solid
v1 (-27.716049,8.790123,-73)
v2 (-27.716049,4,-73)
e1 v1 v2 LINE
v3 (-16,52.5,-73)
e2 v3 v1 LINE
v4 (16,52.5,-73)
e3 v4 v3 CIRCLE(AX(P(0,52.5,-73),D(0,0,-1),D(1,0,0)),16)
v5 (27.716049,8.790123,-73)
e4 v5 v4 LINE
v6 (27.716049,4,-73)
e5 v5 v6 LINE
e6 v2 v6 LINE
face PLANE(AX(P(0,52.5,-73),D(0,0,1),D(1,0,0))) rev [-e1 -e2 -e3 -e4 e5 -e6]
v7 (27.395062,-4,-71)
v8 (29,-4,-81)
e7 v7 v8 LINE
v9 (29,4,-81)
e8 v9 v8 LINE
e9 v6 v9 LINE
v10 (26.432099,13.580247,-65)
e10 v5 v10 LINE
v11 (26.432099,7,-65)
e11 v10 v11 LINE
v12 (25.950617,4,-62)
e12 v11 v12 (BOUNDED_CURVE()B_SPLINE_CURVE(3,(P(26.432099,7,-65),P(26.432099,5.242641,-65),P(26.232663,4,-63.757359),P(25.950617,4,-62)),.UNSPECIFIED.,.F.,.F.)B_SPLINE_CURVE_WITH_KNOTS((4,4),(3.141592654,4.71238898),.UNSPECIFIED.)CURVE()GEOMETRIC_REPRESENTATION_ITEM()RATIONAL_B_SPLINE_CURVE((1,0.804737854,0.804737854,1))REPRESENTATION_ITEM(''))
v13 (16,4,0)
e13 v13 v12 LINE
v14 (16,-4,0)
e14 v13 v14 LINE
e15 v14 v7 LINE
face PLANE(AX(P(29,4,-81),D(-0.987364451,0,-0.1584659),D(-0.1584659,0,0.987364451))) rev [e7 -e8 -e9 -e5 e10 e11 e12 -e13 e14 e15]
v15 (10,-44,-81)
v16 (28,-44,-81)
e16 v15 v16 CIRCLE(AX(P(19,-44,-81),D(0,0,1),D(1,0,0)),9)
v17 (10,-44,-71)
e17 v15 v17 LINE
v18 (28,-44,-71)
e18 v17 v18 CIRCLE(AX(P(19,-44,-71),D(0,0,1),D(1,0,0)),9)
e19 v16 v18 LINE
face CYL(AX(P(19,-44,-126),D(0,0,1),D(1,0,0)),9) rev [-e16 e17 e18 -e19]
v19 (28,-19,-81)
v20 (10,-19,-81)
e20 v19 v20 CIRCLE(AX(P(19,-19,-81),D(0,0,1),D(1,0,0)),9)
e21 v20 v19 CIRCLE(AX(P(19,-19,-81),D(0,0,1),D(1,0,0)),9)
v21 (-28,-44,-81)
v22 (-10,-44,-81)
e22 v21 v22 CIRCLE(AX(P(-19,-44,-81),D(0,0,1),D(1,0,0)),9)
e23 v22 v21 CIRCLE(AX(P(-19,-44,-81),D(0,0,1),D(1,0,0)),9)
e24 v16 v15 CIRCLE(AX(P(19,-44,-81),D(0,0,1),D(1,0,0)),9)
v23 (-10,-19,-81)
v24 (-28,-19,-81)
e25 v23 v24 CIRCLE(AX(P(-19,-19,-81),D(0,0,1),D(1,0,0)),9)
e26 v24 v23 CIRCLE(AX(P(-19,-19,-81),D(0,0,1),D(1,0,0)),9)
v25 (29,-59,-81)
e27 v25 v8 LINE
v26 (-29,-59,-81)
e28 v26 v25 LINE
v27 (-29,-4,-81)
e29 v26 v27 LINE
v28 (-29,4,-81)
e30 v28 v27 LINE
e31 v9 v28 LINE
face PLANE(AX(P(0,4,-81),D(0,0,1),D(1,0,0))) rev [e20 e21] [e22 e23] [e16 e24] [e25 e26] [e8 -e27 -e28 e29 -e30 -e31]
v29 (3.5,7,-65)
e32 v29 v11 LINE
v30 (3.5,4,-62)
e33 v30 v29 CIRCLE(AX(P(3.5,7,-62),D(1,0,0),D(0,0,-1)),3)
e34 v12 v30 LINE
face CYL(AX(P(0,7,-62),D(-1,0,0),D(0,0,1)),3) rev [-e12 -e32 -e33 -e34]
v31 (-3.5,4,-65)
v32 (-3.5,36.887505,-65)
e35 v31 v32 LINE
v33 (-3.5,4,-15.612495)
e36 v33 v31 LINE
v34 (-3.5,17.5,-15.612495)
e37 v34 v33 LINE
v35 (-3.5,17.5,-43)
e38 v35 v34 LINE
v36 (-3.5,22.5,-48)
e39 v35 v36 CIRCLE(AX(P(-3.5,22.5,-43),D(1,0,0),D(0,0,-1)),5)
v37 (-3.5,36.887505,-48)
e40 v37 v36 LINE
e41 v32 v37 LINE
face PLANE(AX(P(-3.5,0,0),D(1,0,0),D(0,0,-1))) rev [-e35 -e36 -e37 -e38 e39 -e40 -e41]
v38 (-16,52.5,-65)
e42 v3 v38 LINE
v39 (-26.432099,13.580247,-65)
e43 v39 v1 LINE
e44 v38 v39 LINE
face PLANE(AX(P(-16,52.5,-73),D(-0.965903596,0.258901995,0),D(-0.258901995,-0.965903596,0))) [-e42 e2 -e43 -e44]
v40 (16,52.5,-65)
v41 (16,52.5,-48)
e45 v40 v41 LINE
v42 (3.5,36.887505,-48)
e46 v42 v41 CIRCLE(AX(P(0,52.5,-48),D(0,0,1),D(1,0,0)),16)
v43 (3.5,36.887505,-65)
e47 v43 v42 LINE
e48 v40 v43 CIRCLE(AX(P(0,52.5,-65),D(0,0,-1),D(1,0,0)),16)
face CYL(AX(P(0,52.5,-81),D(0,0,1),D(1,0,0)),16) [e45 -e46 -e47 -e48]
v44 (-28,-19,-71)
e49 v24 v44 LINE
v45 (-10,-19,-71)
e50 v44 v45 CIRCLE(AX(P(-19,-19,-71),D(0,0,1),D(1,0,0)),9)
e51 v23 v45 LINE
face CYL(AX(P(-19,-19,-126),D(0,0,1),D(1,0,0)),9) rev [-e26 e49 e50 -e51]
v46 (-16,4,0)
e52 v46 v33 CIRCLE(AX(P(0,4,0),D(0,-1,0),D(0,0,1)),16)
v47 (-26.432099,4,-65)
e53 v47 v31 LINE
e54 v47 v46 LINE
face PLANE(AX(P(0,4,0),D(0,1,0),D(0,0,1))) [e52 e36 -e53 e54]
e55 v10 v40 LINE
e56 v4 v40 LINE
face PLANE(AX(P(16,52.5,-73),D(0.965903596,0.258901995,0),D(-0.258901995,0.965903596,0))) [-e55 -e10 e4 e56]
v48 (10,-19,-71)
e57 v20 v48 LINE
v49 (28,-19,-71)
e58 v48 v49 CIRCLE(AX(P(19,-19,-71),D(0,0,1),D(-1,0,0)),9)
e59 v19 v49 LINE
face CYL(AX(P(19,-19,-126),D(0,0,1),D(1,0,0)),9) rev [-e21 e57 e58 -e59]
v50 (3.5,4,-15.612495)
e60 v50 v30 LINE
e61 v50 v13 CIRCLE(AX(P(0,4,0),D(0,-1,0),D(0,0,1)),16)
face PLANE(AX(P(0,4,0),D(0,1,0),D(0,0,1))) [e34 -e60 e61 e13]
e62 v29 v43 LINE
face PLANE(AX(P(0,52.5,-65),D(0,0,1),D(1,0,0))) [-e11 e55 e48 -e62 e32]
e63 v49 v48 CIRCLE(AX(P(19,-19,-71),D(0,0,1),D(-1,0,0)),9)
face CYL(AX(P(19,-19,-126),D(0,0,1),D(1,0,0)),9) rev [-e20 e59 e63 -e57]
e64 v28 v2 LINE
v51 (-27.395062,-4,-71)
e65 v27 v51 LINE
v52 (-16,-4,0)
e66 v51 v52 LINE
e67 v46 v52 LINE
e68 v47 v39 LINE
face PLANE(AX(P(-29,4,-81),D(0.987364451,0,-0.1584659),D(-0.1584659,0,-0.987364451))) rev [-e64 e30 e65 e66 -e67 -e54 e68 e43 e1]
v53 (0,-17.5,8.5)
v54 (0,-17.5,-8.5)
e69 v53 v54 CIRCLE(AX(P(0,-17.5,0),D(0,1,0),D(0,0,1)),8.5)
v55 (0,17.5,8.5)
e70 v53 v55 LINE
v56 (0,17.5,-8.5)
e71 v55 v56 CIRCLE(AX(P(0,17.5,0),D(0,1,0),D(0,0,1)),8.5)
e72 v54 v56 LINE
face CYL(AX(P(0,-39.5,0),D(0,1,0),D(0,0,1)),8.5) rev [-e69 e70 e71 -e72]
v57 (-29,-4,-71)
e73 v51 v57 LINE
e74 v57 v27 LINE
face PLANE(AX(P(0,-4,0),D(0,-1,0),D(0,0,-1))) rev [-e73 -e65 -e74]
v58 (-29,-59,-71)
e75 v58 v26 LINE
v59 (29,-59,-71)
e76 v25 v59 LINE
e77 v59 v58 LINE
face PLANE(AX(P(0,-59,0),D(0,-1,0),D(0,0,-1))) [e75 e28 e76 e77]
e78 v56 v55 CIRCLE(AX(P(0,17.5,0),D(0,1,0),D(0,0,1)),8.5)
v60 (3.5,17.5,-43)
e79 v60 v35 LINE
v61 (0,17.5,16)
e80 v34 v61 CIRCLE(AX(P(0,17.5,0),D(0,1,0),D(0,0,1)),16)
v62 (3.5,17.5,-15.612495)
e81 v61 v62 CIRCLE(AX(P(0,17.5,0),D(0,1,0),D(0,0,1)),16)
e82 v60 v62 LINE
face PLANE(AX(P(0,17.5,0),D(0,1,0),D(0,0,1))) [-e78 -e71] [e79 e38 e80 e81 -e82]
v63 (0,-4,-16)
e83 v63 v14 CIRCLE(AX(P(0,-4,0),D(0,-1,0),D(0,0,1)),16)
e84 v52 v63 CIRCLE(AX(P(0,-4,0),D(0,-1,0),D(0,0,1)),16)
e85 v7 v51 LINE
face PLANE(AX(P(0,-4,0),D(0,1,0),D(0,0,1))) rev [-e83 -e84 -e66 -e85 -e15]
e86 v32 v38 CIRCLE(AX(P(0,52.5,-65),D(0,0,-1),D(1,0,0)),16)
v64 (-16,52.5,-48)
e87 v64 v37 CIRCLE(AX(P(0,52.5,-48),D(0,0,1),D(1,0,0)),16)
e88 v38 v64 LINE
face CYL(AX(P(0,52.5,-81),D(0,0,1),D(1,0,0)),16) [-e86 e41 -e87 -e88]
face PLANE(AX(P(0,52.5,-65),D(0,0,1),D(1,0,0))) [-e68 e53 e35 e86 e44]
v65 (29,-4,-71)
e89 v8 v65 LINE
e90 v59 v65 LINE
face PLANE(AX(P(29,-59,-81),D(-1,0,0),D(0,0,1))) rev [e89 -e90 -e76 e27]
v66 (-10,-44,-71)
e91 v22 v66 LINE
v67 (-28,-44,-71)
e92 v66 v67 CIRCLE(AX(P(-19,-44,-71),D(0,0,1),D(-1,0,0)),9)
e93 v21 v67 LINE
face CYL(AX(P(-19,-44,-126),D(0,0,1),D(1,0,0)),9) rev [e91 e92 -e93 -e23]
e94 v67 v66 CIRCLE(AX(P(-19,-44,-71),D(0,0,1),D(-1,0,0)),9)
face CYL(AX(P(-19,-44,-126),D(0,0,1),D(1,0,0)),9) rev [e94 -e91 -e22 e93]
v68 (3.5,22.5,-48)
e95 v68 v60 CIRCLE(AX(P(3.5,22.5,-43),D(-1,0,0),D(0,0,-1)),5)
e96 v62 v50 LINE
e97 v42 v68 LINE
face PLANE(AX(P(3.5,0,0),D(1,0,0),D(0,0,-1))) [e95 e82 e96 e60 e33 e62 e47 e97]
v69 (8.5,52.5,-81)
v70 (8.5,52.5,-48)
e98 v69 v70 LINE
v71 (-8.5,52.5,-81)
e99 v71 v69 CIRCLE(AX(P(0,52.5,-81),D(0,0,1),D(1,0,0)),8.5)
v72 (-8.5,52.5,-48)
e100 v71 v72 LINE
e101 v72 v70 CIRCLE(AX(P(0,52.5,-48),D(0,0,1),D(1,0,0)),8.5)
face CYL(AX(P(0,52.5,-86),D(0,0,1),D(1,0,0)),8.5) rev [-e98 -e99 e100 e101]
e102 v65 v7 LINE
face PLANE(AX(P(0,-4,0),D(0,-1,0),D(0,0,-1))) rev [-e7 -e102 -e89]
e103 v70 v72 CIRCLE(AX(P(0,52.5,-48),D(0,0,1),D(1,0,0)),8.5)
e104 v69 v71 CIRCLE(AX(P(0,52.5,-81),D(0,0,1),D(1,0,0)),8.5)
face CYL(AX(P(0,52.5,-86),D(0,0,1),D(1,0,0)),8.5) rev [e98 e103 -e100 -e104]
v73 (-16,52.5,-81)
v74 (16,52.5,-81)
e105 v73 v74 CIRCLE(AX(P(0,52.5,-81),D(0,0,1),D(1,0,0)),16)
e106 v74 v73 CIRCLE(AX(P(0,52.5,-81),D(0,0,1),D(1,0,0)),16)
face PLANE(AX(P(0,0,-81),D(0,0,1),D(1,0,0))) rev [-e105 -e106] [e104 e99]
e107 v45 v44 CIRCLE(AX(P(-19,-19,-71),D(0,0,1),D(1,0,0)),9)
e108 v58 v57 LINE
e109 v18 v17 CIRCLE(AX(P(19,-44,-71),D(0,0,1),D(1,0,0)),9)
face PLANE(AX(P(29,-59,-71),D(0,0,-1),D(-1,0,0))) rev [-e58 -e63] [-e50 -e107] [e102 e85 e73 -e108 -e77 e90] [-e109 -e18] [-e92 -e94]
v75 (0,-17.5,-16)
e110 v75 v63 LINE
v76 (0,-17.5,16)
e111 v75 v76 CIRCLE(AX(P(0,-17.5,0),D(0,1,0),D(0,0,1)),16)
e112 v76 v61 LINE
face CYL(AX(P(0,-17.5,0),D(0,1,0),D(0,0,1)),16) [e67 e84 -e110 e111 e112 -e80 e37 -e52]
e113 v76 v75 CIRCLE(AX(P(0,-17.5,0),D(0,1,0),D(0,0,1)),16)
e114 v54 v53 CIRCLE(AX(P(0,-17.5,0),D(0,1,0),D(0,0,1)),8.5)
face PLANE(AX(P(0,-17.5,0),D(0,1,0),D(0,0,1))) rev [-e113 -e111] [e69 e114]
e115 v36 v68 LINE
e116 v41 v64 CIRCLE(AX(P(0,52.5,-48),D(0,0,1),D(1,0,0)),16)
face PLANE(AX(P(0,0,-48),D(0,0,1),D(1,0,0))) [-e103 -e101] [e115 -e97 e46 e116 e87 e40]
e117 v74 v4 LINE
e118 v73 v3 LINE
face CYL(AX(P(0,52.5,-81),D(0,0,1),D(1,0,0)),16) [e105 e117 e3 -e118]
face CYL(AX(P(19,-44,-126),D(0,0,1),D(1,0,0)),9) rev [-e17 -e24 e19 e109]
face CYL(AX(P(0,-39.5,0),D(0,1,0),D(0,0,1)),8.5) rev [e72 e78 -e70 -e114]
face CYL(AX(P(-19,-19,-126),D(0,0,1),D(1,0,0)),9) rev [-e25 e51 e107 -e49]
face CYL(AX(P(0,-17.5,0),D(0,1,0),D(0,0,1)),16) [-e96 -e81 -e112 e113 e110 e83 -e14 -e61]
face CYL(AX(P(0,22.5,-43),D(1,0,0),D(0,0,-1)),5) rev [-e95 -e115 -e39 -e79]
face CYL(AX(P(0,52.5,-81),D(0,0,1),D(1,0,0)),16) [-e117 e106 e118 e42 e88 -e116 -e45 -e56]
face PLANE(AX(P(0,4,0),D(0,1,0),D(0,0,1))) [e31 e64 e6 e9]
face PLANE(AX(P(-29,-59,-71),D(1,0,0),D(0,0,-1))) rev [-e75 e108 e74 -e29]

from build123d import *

# Parameters (mm, degrees)
MAIN_BOSS_SKETCH_32_R    = 16
MAIN_BOSS_32_DEPTH       = 17.5
MAIN_BOSS_BORE_SKETCH_R  = 8.5
MAIN_BOSS_BORE_DEPTH     = 57
LOWER_ARM_PLATE_DEPTH    = 4
UPPER_BOSS_SKETCH_R      = 16
UPPER_BOSS_DEPTH         = 33
UPPER_BOSS_BORE_SKETCH_R = 8.5
UPPER_BOSS_BORE_DEPTH    = 38
UPPER_ARM_PLATE_DEPTH    = 8
PLATE_CUT_SET_A_DEPTH    = 38
PLATE_CUT_SET_B_DEPTH    = 38
RIB_DEPTH                = 3.5
RIB_FILLET_R5_R          = 5
ARM_JUNCTION_FILLET_R3_R = 3
GUSSET_SKETCH_W          = 58
GUSSET_SKETCH_H          = 10
GUSSET_DEPTH             = 55
GUSSET_TRIM_SKETCH_R     = 9
GUSSET_TRIM_CUT_DEPTH    = 55


with BuildPart() as part:
    # Main Boss Sketch Ø32 → Main Boss Ø32 (new, symmetric)
    with BuildSketch(Plane(origin=(0, 0, 0), x_dir=(1, 0, 0), z_dir=(0, 1, 0))):
        with Locations(Location((0, 0, 0), (0, 0, 270))):
            Circle(MAIN_BOSS_SKETCH_32_R)
    extrude(amount=MAIN_BOSS_32_DEPTH, both=True)

    # Main Boss Bore Sketch → Main Boss Bore (cut)
    with BuildSketch(Plane(origin=(0, 17.5, 0), x_dir=(1, 0, 0), z_dir=(0, 1, 0))):
        with Locations(Location((0, 0, 0), (0, 0, 270))):
            Circle(MAIN_BOSS_BORE_SKETCH_R)
    extrude(amount=-MAIN_BOSS_BORE_DEPTH, mode=Mode.SUBTRACT)

    # Lower Arm Sketch → Lower Arm Plate (add, symmetric)
    with BuildSketch(Plane(origin=(0, 0, 0), x_dir=(1, 0, 0), z_dir=(0, 1, 0))):
        with BuildLine():
            Line((0, 81), (29, 81))
            Line((29, 81), (16, 0))
            ThreePointArc((16, 0), (0, 16), (-16, 0))
            Line((-16, 0), (-29, 81))
            Line((-29, 81), (0, 81))
        make_face()
    extrude(amount=LOWER_ARM_PLATE_DEPTH, both=True)



with BuildPart() as body_2:
    # Upper Boss Sketch → Upper Boss (new body)
    with BuildSketch(Plane.XY.offset(-48)):
        with Locations((0, 52.5)):
            Circle(UPPER_BOSS_SKETCH_R)
    extrude(amount=-UPPER_BOSS_DEPTH)

    # Upper Boss Bore Sketch → Upper Boss Bore (cut)
    with BuildSketch(Plane.XY.offset(-48)):
        with Locations((0, 52.5)):
            Circle(UPPER_BOSS_BORE_SKETCH_R)
    extrude(amount=-UPPER_BOSS_BORE_DEPTH, mode=Mode.SUBTRACT)


with BuildPart() as part_1:
    add(part.part)

    add(body_2.part)  # Upper Arm Plate merges body 2
    # Upper Arm Sketch → Upper Arm Plate (add)
    with BuildSketch(Plane.XY.offset(-65)):
        with BuildLine():
            Line((-26.431737368, 4), (29, 4))
            Line((29, 4), (16, 52.5))
            ThreePointArc((16, 52.5), (0, 36.5), (-16, 52.5))
            Line((-16, 52.5), (-29, 4))
            Line((-29, 4), (-26.431737368, 4))
        make_face()
    extrude(amount=-UPPER_ARM_PLATE_DEPTH)

    # Plate Cut Set A Sketch → Plate Cut Set A (cut)
    with BuildSketch(Plane.XZ.offset(4)):
        Polygon((27.716049383, -73), (26.432098765, -65), (29, -65), (29, -73), align=None)
    extrude(amount=-PLATE_CUT_SET_A_DEPTH, mode=Mode.SUBTRACT)

    # Plate Cut Set B Sketch → Plate Cut Set B (cut)
    with BuildSketch(Plane.XZ.offset(4)):
        Polygon((-26.432098765, -65), (-29, -65), (-29, -73), (-27.716049383, -73), align=None)
    extrude(amount=-PLATE_CUT_SET_B_DEPTH, mode=Mode.SUBTRACT)

    # Rib Sketch → Rib (add, symmetric)
    with BuildSketch(Plane(origin=(0, 0, 0), x_dir=(0, 0, -1), z_dir=(1, 0, 0))):
        Polygon((48, 17.5), (11.269108444, 17.5), (11.269108444, 4), (65, 4), (65, 40.002332079), (48, 40.002332079), align=None)
    extrude(amount=RIB_DEPTH, both=True)

    # Rib Fillet R5
    rib_fillet_r5_edges = [part_1.edges().sort_by_distance(p)[0] for p in [
        (0, 17.5, -48),
    ]]
    fillet(rib_fillet_r5_edges, radius=RIB_FILLET_R5_R)

    # Arm Junction Fillet R3
    arm_junction_fillet_r3_edges = [part_1.edges().sort_by_distance(p)[0] for p in [
        (14.966049383, 4, -65),
    ]]
    fillet(arm_junction_fillet_r3_edges, radius=ARM_JUNCTION_FILLET_R3_R)

    # Gusset Sketch → Gusset (add)
    with BuildSketch(Plane.XZ.offset(4)):
        with Locations((0, -76)):
            Rectangle(GUSSET_SKETCH_W, GUSSET_SKETCH_H)
    extrude(amount=GUSSET_DEPTH)

    # Gusset Trim Sketch → Gusset Trim Cut (cut)
    with BuildSketch(Plane.XY.offset(-71)):
        with Locations((19, -44)):
            Circle(GUSSET_TRIM_SKETCH_R)
        with Locations((19, -19)):
            Circle(GUSSET_TRIM_SKETCH_R)
        with Locations((-19, -44)):
            Circle(GUSSET_TRIM_SKETCH_R)
        with Locations((-19, -19)):
            Circle(GUSSET_TRIM_SKETCH_R)
    extrude(amount=-GUSSET_TRIM_CUT_DEPTH, mode=Mode.SUBTRACT)


solid = part_1.part
